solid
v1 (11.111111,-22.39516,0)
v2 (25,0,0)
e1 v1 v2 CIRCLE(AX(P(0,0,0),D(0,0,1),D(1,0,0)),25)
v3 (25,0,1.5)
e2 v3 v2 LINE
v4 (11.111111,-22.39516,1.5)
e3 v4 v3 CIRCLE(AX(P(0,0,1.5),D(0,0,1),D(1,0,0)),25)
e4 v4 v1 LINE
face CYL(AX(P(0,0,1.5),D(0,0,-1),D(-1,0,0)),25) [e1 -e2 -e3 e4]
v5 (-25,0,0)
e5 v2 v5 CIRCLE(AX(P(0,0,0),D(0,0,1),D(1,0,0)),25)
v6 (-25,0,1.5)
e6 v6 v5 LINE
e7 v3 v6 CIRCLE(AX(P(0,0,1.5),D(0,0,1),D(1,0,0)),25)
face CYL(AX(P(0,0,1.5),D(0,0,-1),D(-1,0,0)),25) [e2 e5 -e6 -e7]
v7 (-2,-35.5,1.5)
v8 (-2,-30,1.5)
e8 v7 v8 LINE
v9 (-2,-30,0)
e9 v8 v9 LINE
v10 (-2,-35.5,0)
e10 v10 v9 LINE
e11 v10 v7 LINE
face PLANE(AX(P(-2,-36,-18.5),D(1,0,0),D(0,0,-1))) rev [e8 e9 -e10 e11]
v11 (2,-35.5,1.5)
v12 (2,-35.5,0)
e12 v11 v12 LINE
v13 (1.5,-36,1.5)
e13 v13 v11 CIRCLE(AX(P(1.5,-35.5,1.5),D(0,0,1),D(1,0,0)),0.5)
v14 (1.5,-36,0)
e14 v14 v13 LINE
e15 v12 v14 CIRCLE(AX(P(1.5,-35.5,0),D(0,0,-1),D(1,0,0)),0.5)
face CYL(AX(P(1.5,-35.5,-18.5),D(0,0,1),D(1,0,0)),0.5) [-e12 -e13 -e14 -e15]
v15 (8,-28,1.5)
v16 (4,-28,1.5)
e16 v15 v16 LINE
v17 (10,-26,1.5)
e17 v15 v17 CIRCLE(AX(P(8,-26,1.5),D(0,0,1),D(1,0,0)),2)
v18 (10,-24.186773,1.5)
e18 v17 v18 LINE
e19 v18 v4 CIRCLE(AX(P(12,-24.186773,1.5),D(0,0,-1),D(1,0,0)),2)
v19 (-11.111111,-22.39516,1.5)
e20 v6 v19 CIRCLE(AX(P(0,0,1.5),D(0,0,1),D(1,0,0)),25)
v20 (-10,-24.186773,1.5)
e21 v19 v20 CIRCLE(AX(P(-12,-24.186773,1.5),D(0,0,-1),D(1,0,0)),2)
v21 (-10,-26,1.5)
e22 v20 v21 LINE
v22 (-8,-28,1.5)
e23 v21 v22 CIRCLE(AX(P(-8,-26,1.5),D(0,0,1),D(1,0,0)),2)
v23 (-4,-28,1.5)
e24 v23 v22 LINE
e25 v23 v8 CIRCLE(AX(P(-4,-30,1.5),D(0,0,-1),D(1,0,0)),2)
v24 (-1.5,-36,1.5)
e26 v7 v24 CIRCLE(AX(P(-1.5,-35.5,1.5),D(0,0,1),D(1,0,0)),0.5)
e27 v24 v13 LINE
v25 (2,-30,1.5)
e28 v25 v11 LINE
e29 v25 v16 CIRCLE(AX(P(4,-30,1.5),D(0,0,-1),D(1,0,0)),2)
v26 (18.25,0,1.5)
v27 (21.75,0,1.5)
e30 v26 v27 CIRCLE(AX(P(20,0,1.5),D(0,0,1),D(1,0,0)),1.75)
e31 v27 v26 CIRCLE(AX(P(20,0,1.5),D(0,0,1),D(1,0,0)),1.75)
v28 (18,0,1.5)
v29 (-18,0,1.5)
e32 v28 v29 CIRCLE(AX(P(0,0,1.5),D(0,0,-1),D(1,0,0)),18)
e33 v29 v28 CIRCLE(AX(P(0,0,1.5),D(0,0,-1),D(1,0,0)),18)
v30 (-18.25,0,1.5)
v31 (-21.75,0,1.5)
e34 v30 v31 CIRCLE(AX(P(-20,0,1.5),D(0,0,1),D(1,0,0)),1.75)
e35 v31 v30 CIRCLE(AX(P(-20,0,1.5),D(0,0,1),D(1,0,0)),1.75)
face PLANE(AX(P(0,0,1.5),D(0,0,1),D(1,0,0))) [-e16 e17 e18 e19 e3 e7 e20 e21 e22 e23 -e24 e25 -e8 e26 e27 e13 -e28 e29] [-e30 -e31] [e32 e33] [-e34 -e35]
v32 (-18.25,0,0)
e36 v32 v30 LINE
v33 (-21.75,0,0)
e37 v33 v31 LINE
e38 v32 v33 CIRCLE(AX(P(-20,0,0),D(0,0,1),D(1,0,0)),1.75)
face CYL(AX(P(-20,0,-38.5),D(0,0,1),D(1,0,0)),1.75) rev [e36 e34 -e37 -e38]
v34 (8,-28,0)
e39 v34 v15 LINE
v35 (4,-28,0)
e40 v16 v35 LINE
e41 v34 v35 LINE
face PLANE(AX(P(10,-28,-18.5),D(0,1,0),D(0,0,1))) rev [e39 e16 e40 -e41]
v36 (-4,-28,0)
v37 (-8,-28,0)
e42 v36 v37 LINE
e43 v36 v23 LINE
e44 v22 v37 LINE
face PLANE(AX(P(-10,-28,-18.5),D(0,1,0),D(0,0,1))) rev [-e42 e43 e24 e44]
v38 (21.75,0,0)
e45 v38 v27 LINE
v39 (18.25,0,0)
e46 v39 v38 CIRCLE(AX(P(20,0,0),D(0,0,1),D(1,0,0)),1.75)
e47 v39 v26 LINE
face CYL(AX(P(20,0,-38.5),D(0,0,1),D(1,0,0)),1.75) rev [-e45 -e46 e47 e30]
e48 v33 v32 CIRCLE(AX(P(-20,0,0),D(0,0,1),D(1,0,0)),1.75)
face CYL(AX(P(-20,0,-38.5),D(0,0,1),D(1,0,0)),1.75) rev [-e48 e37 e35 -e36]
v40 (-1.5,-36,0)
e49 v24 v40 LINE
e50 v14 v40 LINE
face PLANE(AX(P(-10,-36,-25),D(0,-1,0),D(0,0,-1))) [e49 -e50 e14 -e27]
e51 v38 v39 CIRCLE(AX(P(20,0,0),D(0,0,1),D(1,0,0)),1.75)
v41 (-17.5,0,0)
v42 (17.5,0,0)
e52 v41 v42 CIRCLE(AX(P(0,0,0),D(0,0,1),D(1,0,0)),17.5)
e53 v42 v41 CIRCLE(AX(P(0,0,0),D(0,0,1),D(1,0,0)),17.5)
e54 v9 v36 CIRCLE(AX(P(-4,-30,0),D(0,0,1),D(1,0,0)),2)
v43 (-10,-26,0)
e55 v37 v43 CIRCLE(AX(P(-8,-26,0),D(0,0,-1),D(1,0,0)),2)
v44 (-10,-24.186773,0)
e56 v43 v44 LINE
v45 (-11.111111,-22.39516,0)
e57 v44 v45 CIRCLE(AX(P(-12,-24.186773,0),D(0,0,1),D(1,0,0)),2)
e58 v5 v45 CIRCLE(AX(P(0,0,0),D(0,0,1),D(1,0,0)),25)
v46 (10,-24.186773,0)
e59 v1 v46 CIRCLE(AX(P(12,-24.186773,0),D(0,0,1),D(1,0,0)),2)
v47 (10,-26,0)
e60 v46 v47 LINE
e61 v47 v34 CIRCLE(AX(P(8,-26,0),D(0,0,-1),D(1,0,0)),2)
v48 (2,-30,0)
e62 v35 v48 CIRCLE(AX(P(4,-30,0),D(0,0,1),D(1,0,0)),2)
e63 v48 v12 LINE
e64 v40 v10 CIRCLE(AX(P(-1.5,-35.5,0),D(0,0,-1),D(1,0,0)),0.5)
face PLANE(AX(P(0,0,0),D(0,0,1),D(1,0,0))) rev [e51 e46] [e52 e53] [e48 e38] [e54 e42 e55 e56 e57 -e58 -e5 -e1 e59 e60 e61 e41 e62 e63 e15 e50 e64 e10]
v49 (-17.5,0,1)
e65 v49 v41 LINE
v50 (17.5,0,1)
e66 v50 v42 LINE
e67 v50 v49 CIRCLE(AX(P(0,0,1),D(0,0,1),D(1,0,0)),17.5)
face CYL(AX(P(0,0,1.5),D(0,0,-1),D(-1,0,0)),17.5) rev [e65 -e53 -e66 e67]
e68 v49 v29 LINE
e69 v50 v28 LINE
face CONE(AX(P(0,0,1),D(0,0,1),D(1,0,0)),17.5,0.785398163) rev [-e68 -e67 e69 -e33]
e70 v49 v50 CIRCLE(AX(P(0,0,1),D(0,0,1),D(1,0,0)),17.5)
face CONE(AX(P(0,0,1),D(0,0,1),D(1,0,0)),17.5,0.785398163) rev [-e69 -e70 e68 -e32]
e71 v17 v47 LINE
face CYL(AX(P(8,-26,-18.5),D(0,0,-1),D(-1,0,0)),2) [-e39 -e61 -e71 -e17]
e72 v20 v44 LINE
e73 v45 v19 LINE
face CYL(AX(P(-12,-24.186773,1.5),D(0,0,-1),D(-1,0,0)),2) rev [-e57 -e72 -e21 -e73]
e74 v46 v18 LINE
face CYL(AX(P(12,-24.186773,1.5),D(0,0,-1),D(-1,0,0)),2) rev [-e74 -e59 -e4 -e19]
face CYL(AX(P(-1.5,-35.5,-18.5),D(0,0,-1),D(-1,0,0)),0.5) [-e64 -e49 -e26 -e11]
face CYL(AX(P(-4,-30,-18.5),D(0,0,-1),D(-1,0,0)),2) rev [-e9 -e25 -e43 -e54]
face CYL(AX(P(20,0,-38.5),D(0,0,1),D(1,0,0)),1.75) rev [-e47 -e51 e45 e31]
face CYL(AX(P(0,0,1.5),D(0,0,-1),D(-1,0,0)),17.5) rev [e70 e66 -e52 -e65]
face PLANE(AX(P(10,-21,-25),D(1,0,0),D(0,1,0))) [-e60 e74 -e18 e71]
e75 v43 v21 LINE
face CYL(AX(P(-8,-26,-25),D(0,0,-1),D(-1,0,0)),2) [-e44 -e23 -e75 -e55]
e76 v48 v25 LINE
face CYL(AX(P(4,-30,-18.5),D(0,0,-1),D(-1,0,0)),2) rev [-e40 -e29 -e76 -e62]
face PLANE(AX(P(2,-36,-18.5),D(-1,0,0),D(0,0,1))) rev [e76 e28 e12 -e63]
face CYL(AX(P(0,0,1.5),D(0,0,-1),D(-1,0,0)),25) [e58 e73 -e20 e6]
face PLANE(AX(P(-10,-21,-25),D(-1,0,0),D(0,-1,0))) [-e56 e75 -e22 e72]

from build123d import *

# Parameters (mm, degrees)
SKETCH_1_R          = 25
SKETCH_1_R_2        = 17.5
EXTRUDE_1_DEPTH     = 1.5
SKETCH_4_W          = 20
SKETCH_4_H          = 15
EXTRUDE_2_DEPTH     = 1.5
SKETCH_5_W          = 8
SKETCH_5_H          = 8
CUT_EXTRUDE_3_DEPTH = 20
FILLET_2_R          = 2
SKETCH_6_R          = 1.75
CUT_EXTRUDE_4_DEPTH = 40
FILLET_3_R          = 0.5
CHAMFER_1_SIZE      = 0.5


with BuildPart() as part:
    # 草图1 → 凸台-拉伸1 (new body)
    with BuildSketch(Plane.XY):
        Circle(SKETCH_1_R)
        Circle(SKETCH_1_R_2, mode=Mode.SUBTRACT)
    extrude(amount=EXTRUDE_1_DEPTH)

    # 草图4 → 凸台-拉伸2 (add)
    with BuildSketch(Plane.XY.offset(1.5)):
        with Locations((0, -28.5)):
            Rectangle(SKETCH_4_W, SKETCH_4_H)
    extrude(amount=-EXTRUDE_2_DEPTH)

    # 草图5 → 切除-拉伸3 (cut)
    with BuildSketch(Plane.XY.offset(1.5)):
        with Locations((-6, -32)):
            Rectangle(SKETCH_5_W, SKETCH_5_H)
        with Locations((6, -32)):
            Rectangle(SKETCH_5_W, SKETCH_5_H)
    extrude(amount=-CUT_EXTRUDE_3_DEPTH, mode=Mode.SUBTRACT)

    # 圆角2
    fillet_2_edges = [part.edges().sort_by_distance(p)[0] for p in [
        (10, -22.912878475, 0.75),
        (-10, -22.912878475, 0.75),
        (-10, -28, 0.75),
        (-2, -28, 0.75),
        (2, -28, 0.75),
        (10, -28, 0.75),
    ]]
    fillet(fillet_2_edges, radius=FILLET_2_R)

    # 草图6 → 切除-拉伸4 (cut)
    with BuildSketch(Plane.XY.offset(1.5)):
        with Locations((-20, 0)):
            Circle(SKETCH_6_R)
        with Locations((20, 0)):
            Circle(SKETCH_6_R)
    extrude(amount=-CUT_EXTRUDE_4_DEPTH, mode=Mode.SUBTRACT)

    # 圆角3
    fillet_3_edges = [part.edges().sort_by_distance(p)[0] for p in [
        (-2, -36, 0.75),
        (2, -36, 0.75),
    ]]
    fillet(fillet_3_edges, radius=FILLET_3_R)

    # 倒角1
    chamfer_1_edges = [part.edges().sort_by_distance(p)[0] for p in [
        (-17.5, 0, 1.5),
    ]]
    chamfer(chamfer_1_edges, length=CHAMFER_1_SIZE)


solid = part.part
